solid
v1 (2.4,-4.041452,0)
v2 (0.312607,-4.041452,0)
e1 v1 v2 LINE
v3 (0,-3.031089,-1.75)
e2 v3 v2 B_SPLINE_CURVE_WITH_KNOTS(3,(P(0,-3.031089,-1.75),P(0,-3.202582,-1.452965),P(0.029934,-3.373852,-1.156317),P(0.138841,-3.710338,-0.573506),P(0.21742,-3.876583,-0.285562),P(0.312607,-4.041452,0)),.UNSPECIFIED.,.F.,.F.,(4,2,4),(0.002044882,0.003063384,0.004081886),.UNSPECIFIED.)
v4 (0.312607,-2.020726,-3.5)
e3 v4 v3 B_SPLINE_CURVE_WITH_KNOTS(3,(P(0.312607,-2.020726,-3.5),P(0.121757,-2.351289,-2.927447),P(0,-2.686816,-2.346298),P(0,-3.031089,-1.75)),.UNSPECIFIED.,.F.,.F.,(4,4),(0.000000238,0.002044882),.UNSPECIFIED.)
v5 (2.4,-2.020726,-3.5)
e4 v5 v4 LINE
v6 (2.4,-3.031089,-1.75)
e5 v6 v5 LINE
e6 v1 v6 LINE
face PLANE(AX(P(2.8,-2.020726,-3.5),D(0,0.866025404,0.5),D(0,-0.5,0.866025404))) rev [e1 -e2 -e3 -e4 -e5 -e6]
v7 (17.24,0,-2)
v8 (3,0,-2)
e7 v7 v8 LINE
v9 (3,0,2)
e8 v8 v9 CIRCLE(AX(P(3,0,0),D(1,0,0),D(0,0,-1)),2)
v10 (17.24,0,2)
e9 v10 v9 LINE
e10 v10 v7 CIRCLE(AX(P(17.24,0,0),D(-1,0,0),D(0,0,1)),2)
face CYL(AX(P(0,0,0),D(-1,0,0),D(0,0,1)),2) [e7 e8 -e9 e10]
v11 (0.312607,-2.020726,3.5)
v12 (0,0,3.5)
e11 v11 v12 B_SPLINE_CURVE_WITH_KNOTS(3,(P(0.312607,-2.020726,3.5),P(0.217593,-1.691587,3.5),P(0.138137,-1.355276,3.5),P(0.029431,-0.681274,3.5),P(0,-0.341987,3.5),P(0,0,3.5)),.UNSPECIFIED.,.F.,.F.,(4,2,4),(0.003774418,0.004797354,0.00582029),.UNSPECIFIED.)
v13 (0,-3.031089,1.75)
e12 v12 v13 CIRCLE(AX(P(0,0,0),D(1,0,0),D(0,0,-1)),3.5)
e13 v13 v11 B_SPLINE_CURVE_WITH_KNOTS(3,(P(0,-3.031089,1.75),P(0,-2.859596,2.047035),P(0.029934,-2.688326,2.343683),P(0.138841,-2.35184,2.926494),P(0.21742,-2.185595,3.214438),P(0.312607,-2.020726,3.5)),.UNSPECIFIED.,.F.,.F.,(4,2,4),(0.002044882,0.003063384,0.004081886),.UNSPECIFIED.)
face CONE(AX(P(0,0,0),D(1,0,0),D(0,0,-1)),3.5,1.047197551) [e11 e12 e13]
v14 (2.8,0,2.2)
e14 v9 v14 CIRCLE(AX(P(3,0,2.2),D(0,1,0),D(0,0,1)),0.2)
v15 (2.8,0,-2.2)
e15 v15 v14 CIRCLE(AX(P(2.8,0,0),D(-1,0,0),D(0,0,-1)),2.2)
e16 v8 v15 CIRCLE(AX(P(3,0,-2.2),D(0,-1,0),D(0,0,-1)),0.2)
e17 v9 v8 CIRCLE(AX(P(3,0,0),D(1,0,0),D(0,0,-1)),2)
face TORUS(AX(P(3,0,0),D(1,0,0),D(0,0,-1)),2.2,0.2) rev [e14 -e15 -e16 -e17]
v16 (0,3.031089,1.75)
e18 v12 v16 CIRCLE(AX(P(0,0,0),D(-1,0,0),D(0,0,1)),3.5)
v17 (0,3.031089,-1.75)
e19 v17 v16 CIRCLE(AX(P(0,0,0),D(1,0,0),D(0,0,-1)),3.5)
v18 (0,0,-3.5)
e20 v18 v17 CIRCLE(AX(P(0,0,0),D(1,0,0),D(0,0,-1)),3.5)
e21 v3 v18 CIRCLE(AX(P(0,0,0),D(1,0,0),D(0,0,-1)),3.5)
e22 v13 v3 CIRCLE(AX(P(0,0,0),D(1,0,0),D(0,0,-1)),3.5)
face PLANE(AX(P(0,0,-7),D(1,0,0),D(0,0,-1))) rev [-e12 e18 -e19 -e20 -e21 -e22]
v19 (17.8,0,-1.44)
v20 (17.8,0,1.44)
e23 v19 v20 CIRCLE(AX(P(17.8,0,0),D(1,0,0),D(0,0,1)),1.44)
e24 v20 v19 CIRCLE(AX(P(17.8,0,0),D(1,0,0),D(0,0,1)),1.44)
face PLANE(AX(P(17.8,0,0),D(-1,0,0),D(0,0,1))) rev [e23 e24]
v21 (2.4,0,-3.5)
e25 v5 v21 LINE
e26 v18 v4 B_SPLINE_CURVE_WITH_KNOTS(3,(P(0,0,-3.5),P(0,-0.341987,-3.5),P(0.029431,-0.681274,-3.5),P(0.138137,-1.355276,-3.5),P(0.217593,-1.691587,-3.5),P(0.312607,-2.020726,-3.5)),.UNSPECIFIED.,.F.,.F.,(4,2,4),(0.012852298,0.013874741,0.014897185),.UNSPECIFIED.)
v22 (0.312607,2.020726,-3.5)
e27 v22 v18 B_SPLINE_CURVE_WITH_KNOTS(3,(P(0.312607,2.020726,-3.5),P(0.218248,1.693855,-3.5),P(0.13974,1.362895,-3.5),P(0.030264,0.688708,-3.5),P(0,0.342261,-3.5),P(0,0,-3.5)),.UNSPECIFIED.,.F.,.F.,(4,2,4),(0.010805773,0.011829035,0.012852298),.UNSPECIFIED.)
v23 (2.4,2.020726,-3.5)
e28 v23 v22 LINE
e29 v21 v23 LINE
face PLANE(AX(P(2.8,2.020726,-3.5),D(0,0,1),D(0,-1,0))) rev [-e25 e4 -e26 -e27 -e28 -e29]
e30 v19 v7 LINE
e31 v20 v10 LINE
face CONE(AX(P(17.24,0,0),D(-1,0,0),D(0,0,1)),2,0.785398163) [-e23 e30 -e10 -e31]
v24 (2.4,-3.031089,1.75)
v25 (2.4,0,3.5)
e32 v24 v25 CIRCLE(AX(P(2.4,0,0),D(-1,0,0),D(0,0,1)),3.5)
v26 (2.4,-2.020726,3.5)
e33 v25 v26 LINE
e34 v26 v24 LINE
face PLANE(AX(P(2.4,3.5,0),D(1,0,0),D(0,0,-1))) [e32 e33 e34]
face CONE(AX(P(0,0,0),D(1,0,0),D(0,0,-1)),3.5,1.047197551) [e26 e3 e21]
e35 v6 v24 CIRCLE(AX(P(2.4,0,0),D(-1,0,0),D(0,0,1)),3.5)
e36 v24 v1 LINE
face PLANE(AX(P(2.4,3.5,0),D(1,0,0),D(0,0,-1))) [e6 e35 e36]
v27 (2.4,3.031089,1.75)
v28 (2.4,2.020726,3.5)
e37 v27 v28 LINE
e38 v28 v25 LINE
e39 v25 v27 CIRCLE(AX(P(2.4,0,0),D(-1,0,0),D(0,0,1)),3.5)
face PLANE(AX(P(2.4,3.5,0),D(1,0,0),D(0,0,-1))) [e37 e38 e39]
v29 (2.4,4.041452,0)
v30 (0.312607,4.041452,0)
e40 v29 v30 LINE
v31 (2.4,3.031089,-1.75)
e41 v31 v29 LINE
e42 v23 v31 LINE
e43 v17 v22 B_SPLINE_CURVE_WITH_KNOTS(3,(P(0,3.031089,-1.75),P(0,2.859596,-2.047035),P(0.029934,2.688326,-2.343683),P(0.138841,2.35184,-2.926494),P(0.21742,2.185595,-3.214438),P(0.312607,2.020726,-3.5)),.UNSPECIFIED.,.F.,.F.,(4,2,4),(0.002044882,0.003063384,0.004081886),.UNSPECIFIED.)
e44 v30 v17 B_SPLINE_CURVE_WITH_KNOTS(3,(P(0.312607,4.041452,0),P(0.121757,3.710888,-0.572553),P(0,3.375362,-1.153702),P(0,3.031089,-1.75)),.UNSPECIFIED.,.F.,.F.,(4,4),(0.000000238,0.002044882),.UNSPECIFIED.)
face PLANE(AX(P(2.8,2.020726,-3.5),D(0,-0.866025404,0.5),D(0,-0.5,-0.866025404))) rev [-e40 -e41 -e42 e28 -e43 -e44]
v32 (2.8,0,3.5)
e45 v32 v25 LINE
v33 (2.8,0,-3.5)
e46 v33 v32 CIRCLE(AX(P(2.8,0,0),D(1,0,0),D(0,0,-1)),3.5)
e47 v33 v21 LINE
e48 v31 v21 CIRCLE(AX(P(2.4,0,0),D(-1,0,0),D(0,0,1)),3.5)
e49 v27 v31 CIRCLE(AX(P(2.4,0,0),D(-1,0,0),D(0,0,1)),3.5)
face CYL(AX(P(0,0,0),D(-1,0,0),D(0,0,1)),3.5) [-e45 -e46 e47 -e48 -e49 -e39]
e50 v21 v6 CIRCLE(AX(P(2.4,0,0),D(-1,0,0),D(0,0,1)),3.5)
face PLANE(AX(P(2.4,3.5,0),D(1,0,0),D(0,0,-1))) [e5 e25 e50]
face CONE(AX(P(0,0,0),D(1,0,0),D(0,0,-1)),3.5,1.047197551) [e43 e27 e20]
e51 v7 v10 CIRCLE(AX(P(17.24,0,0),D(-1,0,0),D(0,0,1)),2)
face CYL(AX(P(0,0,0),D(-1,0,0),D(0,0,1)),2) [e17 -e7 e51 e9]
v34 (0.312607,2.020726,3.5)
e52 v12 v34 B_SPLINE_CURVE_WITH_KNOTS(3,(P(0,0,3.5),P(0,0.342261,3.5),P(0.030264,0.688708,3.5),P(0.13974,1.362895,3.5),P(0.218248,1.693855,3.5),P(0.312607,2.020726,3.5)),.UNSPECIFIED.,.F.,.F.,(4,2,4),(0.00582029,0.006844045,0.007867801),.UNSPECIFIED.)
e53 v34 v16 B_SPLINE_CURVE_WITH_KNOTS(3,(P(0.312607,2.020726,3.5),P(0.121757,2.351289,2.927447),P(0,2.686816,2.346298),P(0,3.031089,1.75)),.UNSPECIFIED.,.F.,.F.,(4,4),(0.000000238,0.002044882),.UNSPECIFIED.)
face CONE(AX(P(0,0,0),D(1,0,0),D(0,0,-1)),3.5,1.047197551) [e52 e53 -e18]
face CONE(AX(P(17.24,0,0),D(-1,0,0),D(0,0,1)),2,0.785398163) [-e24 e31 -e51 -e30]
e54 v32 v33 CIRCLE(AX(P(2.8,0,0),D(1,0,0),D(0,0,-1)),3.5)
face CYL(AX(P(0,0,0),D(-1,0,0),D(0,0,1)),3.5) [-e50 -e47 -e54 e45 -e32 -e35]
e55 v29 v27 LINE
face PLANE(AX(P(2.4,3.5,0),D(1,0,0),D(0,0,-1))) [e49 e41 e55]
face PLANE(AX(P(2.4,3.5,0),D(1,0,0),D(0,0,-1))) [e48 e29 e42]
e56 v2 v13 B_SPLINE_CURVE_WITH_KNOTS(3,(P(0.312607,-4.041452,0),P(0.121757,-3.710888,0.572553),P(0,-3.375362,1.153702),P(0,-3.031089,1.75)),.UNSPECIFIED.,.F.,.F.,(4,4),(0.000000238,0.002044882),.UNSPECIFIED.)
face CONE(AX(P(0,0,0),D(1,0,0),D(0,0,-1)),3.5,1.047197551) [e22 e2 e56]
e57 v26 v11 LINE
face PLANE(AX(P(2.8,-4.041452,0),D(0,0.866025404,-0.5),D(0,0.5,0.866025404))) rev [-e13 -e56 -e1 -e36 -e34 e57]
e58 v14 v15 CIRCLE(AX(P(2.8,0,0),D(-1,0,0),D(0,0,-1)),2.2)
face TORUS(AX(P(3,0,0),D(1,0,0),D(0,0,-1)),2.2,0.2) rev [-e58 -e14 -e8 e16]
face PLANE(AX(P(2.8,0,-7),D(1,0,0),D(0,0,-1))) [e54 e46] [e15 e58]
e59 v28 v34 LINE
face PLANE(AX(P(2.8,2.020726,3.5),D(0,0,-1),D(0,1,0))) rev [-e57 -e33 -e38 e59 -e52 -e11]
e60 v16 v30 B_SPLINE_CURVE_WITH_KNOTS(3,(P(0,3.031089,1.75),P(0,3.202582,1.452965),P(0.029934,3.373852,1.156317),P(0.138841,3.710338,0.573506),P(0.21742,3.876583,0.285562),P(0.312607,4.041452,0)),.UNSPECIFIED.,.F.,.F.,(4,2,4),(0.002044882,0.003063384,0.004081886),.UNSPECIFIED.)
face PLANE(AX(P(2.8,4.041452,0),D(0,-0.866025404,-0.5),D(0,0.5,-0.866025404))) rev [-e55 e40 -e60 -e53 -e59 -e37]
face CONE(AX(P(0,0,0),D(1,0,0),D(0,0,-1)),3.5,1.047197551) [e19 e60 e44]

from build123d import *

# Parameters (mm, degrees)
EXTRUDE_358_DEPTH = 2.8
SKETCH_4_W        = 0.4
SKETCH_4_H        = 10.541451884
CHAMFER_1889_SIZE = 0.56
FILLET_1942_R     = 0.2


with BuildPart() as part:
    # 草图1 → Extrude 358 (new body)
    with BuildSketch(Plane(origin=(0, 0, 0), x_dir=(0, 0, -1), z_dir=(1, 0, 0))):
        Polygon((3.5, 2.020725942), (3.5, -2.020725942), (0, -4.041451884), (-3.5, -2.020725942), (-3.5, 2.020725942), (0, 4.041451884), align=None)
    extrude(amount=EXTRUDE_358_DEPTH)

    # 草图2 → 凸台-旋转1 (revolve)
    with BuildSketch(Plane.XY, mode=Mode.PRIVATE) as revolve_1_sk:
        Polygon((0, 0), (17.8, 0), (17.8, 1.3938), (17.8, 2), (0, 2), align=None)
    revolve(revolve_1_sk.sketch.rotate(Axis((0, 0, 0), (1, 0, 0)), 90), axis=Axis((0, 0, 0), (1, 0, 0)))

    # 草图3 → 切除-旋转1 (revolve, cut)
    with BuildSketch(Plane.XY):
        Polygon((0, 3.5), (3.199358737, 9.041451884), (3.199358737, 14.041451884), (-10, 14.041451884), (-10, 3.5), align=None)
    revolve(axis=Axis((0, 0, 0), (1, 0, 0)), mode=Mode.SUBTRACT)

    # 草图5 → 切除-旋转2 (revolve, cut)
    with BuildSketch(Plane.XY):
        Polygon((2.8, 3.5), (-0.399358737, 9.041451884), (-0.399358737, 14.041451884), (9.600641263, 14.041451884), (9.600641263, 3.5), align=None)
    revolve(axis=Axis((0, 0, 0), (1, 0, 0)), mode=Mode.SUBTRACT)

    # 草图4 → 切除-旋转3 (revolve, cut)
    with BuildSketch(Plane.XY, mode=Mode.PRIVATE) as cut_revolve_3_sk:
        with Locations((2.6, 8.770725942)):
            Rectangle(SKETCH_4_W, SKETCH_4_H)
    revolve(cut_revolve_3_sk.sketch.rotate(Axis((0, 0, 0), (1, 0, 0)), 270), axis=Axis((0, 0, 0), (1, 0, 0)), mode=Mode.SUBTRACT)

    # Chamfer 1889
    chamfer_1889_edges = [part.edges().sort_by_distance(p)[0] for p in [
        (17.8, 0, -2),
    ]]
    chamfer(chamfer_1889_edges, length=CHAMFER_1889_SIZE)

    # Fillet 1942
    fillet_1942_edges = [part.edges().sort_by_distance(p)[0] for p in [
        (2.8, 0, -2),
    ]]
    fillet(fillet_1942_edges, radius=FILLET_1942_R)


solid = part.part
